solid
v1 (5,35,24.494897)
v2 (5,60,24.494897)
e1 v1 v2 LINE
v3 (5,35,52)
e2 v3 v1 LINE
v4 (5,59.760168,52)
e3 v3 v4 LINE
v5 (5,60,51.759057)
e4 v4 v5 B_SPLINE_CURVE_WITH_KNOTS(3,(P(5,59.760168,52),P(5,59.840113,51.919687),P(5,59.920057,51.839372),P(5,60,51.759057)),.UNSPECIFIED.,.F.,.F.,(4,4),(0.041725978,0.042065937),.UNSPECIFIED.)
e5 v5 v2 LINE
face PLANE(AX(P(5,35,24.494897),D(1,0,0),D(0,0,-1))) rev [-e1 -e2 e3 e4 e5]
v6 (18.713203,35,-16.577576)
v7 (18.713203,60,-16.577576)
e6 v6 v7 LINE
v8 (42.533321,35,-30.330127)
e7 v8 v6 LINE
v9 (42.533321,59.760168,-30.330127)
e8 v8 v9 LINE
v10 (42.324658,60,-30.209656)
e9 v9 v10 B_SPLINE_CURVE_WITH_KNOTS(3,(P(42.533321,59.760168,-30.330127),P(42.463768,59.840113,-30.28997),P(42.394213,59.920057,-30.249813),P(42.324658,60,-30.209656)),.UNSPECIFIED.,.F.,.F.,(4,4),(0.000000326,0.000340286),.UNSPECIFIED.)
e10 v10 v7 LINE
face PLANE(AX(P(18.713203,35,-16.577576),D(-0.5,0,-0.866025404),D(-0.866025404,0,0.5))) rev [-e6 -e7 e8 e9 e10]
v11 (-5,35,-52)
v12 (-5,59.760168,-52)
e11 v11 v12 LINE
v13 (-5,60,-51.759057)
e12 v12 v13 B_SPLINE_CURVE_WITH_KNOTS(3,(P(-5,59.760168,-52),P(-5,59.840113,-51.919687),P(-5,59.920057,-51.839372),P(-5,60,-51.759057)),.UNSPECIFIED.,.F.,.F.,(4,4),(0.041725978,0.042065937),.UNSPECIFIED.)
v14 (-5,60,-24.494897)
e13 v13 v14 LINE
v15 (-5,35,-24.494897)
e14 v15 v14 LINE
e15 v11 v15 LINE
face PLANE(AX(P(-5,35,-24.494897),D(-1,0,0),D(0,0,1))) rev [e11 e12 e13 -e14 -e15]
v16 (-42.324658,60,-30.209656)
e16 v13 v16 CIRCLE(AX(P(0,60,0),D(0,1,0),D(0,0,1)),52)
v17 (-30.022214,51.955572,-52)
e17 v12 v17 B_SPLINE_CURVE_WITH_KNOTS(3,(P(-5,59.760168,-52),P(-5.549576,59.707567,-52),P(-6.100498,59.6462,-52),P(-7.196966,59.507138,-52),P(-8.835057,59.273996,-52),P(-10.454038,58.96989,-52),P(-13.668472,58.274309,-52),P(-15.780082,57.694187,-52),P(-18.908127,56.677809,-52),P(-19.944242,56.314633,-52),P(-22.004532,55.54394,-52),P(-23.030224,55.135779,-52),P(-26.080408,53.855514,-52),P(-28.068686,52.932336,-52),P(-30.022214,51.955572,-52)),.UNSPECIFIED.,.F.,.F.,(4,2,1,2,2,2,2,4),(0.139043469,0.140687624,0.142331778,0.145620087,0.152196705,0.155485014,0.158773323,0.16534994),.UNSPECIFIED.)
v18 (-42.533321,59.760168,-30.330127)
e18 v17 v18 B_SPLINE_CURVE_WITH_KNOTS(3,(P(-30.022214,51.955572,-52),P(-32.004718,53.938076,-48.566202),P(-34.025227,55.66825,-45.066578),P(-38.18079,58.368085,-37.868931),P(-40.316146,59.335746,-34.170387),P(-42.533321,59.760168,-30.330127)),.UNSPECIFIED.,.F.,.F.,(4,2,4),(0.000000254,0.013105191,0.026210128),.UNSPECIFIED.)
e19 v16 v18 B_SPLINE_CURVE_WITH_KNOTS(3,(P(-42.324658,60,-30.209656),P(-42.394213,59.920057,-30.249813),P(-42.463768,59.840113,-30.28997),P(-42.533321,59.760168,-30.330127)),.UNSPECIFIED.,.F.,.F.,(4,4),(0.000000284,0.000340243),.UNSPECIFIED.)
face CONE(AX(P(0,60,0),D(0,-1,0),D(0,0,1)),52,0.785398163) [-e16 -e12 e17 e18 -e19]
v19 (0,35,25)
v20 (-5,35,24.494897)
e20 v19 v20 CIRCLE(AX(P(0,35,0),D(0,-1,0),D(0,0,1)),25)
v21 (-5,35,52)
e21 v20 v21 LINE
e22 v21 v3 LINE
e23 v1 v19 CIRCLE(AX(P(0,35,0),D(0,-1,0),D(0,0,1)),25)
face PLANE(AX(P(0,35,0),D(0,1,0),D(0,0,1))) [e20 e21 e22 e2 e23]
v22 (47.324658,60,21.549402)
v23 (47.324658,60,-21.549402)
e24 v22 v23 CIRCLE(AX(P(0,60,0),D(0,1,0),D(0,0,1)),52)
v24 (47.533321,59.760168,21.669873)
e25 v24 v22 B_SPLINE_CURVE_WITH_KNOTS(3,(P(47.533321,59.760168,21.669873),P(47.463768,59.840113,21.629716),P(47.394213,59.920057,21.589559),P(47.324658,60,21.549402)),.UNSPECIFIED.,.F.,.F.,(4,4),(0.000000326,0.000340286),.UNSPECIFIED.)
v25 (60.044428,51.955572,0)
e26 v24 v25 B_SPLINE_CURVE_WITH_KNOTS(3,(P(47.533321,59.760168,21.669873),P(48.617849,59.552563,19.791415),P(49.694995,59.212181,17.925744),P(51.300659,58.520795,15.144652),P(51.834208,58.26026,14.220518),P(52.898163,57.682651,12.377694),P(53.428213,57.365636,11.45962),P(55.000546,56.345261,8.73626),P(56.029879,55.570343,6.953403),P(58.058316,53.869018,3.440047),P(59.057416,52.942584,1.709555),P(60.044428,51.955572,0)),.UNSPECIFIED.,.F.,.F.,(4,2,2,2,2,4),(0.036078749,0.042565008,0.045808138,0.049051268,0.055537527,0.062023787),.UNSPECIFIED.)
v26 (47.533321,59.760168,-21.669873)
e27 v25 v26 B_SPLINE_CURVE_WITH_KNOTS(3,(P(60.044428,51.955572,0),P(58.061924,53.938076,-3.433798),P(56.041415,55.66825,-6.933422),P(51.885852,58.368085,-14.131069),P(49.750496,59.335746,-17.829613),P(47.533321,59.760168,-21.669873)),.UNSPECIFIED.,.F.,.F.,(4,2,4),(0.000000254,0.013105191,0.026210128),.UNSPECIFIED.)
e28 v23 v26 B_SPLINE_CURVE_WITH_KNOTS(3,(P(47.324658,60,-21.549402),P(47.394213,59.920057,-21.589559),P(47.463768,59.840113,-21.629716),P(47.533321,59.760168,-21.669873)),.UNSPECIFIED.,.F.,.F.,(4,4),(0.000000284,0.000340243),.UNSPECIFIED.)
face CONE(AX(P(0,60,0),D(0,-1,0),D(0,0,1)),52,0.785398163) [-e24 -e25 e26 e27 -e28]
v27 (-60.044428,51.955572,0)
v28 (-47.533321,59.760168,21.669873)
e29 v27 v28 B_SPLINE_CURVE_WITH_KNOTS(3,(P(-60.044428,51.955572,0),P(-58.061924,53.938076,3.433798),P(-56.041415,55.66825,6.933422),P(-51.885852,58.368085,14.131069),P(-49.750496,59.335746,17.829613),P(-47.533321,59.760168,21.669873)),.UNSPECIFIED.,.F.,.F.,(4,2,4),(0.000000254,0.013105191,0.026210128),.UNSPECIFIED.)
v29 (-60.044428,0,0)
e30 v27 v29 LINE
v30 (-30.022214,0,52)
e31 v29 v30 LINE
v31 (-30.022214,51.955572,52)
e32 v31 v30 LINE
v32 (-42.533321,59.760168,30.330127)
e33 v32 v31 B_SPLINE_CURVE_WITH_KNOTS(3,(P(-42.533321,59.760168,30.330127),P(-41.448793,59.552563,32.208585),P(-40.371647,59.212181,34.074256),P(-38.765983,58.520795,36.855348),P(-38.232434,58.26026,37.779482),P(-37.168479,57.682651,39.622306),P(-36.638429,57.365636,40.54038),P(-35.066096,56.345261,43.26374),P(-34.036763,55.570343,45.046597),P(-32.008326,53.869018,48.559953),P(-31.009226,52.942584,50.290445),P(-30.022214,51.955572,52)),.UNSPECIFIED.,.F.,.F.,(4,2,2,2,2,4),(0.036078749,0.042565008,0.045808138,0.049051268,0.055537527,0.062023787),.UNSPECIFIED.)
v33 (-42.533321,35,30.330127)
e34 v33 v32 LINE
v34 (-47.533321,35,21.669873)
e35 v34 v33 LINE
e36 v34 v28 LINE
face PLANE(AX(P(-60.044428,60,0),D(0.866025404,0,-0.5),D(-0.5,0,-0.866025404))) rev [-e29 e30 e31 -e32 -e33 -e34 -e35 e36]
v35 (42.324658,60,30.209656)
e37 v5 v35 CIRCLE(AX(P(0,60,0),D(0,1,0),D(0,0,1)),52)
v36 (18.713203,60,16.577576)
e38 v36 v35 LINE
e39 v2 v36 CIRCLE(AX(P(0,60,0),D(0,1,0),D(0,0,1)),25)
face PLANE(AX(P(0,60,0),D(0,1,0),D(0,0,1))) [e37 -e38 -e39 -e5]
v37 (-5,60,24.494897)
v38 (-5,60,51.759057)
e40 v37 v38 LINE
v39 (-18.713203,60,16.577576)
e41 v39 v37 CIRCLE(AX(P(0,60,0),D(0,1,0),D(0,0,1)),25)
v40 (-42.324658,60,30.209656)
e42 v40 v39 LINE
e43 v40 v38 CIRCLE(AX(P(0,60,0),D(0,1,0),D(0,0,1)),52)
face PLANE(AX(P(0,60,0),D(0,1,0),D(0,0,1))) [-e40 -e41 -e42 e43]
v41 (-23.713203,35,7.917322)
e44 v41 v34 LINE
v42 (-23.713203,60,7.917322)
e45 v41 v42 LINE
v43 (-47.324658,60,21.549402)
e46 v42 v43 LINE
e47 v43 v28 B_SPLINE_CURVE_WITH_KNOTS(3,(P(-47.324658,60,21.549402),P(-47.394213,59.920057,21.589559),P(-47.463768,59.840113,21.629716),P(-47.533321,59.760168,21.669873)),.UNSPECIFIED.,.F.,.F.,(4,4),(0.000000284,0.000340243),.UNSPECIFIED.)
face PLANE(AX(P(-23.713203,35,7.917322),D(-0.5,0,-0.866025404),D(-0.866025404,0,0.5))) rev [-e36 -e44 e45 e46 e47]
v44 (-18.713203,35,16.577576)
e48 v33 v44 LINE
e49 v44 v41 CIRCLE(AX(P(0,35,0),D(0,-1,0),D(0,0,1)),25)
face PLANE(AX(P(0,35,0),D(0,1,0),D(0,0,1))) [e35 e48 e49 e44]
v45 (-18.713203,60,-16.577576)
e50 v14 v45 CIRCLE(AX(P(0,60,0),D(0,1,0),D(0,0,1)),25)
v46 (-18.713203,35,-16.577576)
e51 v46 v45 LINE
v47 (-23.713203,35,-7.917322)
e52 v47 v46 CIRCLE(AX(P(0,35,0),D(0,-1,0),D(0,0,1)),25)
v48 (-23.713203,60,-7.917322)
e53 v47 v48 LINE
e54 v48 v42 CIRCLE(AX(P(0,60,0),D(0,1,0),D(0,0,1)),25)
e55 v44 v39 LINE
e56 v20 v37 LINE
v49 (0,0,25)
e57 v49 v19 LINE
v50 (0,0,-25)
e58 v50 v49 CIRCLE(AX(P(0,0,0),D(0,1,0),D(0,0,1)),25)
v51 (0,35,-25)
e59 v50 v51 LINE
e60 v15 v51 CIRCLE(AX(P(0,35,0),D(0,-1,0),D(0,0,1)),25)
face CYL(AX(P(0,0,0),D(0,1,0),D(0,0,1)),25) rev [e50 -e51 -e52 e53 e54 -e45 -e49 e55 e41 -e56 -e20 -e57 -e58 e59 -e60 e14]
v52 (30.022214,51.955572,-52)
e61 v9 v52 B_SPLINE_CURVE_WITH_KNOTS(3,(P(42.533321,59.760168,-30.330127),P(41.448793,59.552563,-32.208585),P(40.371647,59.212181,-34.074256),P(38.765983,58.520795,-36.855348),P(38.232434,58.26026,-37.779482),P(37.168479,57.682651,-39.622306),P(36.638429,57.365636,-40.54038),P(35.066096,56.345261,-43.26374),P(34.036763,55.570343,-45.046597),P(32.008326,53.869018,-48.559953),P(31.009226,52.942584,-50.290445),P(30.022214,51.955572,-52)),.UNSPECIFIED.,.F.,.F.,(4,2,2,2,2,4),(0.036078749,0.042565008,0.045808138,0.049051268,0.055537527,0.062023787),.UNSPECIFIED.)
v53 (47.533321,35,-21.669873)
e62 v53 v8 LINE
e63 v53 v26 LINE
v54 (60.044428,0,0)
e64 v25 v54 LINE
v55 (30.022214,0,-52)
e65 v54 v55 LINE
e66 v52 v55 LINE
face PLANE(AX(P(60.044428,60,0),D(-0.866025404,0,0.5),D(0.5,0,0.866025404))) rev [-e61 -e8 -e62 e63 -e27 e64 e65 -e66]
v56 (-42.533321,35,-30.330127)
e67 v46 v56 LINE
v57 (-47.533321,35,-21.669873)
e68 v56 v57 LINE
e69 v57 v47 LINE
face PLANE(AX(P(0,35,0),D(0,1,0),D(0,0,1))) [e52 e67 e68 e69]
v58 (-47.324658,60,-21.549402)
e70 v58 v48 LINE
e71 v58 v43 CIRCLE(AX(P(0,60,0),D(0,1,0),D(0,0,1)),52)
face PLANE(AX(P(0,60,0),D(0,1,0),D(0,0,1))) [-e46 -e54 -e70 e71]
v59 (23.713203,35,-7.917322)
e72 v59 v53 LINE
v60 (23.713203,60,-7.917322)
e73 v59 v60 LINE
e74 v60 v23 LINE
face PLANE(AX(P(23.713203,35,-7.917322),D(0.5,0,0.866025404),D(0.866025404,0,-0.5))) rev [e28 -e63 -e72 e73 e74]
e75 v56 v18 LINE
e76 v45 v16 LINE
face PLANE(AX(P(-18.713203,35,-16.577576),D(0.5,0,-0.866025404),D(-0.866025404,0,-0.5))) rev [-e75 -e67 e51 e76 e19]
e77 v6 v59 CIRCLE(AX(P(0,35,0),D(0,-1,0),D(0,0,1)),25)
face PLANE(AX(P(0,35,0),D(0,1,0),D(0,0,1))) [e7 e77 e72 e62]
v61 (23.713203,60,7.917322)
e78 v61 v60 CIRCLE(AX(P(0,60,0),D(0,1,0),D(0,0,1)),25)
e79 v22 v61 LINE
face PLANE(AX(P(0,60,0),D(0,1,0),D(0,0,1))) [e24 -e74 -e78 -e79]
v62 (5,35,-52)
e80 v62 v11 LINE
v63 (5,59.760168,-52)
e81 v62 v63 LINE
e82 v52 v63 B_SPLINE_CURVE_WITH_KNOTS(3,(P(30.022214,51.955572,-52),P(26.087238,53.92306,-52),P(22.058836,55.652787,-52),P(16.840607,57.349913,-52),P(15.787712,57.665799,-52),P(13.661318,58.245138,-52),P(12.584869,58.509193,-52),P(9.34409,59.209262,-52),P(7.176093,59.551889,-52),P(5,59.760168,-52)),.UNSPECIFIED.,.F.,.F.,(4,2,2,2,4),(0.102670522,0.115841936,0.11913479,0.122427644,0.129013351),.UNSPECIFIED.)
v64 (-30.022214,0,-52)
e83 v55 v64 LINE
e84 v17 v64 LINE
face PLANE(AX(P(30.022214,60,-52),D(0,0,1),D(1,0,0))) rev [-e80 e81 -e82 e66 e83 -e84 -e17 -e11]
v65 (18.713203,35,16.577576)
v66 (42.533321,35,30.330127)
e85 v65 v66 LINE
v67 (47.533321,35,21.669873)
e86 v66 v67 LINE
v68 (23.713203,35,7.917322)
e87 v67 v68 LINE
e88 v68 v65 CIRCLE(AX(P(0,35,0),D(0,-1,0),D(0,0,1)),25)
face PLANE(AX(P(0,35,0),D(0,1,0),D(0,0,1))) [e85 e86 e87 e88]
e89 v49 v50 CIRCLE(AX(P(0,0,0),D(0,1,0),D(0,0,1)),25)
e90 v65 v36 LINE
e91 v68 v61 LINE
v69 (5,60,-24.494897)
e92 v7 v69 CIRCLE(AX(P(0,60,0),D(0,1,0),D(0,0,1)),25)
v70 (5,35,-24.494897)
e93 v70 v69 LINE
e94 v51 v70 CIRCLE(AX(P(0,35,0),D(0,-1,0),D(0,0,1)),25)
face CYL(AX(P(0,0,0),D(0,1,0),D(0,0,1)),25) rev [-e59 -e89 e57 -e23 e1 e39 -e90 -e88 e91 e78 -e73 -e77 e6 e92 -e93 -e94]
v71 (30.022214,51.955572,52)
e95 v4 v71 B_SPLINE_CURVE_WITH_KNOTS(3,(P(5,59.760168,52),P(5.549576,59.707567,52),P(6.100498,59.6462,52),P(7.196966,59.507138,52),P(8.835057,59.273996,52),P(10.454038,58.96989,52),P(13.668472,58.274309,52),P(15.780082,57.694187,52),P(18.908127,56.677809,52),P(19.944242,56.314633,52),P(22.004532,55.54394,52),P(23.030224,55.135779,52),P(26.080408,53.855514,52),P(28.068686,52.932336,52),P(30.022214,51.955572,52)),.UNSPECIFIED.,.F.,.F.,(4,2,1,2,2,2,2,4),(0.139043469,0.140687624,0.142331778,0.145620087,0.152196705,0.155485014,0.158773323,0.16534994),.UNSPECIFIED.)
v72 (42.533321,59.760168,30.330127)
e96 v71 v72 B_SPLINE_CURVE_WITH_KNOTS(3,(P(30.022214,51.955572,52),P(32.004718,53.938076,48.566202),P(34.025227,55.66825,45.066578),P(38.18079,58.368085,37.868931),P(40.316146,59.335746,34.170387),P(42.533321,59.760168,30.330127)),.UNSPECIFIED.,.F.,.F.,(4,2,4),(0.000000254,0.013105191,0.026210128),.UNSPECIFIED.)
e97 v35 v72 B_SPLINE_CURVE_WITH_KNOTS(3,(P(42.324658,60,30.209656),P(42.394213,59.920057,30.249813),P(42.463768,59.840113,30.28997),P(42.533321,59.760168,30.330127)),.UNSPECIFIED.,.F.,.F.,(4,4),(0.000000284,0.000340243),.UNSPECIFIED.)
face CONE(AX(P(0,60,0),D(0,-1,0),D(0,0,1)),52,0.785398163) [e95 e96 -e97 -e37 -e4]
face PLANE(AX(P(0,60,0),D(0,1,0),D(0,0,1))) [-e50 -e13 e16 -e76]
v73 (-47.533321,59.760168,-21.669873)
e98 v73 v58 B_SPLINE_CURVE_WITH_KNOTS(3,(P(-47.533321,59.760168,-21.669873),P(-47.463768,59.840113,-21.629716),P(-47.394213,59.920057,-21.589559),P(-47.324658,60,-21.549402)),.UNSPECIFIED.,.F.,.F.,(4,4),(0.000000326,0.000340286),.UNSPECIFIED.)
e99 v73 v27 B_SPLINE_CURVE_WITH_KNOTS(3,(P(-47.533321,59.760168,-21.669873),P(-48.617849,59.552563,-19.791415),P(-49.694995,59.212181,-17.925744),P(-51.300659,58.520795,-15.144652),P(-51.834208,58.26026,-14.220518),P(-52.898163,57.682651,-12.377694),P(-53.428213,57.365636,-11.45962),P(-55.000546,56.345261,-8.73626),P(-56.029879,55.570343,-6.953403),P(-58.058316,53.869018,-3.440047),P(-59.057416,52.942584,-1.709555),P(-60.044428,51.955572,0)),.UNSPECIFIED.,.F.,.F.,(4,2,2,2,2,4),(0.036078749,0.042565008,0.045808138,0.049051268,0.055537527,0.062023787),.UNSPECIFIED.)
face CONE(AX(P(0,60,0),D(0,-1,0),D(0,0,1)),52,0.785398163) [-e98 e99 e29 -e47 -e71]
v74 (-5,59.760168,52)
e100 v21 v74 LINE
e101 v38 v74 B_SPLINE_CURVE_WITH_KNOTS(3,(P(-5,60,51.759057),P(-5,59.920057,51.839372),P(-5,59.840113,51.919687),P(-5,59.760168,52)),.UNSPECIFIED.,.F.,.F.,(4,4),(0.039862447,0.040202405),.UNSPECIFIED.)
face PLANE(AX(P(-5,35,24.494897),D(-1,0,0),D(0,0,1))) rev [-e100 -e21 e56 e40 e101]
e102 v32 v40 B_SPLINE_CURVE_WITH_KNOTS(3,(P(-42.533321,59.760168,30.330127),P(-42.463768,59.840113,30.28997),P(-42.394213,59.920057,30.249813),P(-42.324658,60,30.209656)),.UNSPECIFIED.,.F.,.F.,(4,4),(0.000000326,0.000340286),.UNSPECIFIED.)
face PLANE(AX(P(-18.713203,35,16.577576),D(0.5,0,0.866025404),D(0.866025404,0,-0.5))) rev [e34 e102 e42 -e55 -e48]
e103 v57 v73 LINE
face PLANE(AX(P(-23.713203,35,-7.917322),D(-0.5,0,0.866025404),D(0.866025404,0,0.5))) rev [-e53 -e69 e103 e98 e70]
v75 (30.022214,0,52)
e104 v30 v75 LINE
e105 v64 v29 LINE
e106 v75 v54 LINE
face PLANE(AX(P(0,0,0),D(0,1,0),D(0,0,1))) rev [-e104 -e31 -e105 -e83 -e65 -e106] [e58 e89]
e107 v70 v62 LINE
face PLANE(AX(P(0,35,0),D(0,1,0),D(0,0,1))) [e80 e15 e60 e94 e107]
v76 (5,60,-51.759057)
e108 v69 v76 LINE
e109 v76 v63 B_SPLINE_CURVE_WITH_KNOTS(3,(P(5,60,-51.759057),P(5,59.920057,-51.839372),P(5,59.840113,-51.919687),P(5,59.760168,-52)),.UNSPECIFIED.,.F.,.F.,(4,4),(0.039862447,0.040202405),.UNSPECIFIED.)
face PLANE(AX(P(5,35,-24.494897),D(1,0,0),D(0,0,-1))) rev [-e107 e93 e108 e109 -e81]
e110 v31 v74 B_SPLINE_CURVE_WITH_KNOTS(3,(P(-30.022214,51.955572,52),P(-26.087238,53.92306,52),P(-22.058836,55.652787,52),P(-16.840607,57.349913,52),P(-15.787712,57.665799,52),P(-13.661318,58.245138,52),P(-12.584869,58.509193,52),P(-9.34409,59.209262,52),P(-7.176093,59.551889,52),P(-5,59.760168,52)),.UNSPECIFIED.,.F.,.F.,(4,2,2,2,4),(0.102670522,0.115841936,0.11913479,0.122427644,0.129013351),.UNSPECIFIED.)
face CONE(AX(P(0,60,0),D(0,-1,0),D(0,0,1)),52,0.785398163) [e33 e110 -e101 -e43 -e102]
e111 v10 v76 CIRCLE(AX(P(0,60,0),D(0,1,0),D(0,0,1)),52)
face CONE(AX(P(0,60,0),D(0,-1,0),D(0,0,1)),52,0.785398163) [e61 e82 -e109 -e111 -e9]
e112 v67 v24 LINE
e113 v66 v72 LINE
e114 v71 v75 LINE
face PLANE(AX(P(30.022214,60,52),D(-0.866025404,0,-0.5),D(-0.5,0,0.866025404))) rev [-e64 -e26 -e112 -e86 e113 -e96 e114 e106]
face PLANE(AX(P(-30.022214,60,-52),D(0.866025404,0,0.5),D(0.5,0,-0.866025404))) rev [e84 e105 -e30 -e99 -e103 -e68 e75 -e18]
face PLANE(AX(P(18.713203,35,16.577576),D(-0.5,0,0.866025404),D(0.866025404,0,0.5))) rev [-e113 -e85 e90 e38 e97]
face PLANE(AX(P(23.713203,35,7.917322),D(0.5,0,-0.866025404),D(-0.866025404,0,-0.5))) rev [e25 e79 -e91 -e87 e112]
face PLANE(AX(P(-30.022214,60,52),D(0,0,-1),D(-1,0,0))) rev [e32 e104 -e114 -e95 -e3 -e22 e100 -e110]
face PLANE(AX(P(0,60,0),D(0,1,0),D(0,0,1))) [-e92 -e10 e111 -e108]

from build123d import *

# Parameters (mm, degrees)
HEX_BODY_104AF_X_60_DEPTH      = 60
CROWN_CHAMFER_SKETCH_OUTSIDE_W = 276.052
CROWN_CHAMFER_SKETCH_OUTSIDE_H = 259.964
CROWN_CHAMFER_SKETCH_OUTSIDE_R = 52
CROWN_CHAMFER_45DEG_DEPTH      = 60
CROWN_CHAMFER_45DEG_DRAFT      = -45
BORE_SKETCH_50_R               = 25
BORE_50_DEPTH                  = 60
CASTLE_SLOTS_6X10_DEPTH        = 25


with BuildPart() as part:
    # Hex Profile Sketch → Hex Body 104AF x 60 (new body)
    with BuildSketch(Plane(origin=(0, 0, 0), x_dir=(1, 0, 0), z_dir=(0, 1, 0))):
        Polygon((30.022213998, -52), (60.044427996, 0), (30.022213998, 52), (-30.022213998, 52), (-60.044427996, 0), (-30.022213998, -52), align=None)
    extrude(amount=HEX_BODY_104AF_X_60_DEPTH)


with BuildPart() as crown_chamfer_45deg_tool:
    # Crown Chamfer Sketch outside → Crown Chamfer 45deg (with draft: the straight prism first)
    with BuildSketch(Plane(origin=(0, 60, 0), x_dir=(1, 0, 0), z_dir=(0, 1, 0))):
        Rectangle(CROWN_CHAMFER_SKETCH_OUTSIDE_W, CROWN_CHAMFER_SKETCH_OUTSIDE_H)
        Circle(CROWN_CHAMFER_SKETCH_OUTSIDE_R, mode=Mode.SUBTRACT)
    extrude(amount=-CROWN_CHAMFER_45DEG_DEPTH)
    # Crown Chamfer 45deg: the draft: its side faces are tilted about the plane it starts from
    crown_chamfer_45deg_sides = [crown_chamfer_45deg_tool.faces().sort_by_distance(p)[0] for p in [
        (0, 30, 129.982),
        (138.026, 30, 0),
        (0, 30, -129.982),
        (-138.026, 30, 0),
        (-52, 30, 0),
    ]]
    draft(crown_chamfer_45deg_sides, Plane(origin=(0, 60, 0), x_dir=(1, 0, 0), z_dir=(0, 1, 0)), CROWN_CHAMFER_45DEG_DRAFT)


with BuildPart() as part_1:
    add(part.part)

    # Crown Chamfer 45deg: cut by crown_chamfer_45deg_tool
    add(crown_chamfer_45deg_tool.part, mode=Mode.SUBTRACT)

    # Bore Sketch Ø50 → Bore Ø50 (cut)
    with BuildSketch(Plane(origin=(0, 60, 0), x_dir=(1, 0, 0), z_dir=(0, 1, 0))):
        with Locations(Location((0, 0, 0), (0, 0, 270))):
            Circle(BORE_SKETCH_50_R)
    extrude(amount=-BORE_50_DEPTH, mode=Mode.SUBTRACT)

    # Castle Slots Sketch → Castle Slots 6x10 (cut)
    with BuildSketch(Plane(origin=(0, 60, 0), x_dir=(1, 0, 0), z_dir=(0, 1, 0))):
        with BuildLine():
            Line((-5, -24.494897428), (-5, -52))
            Line((-5, -52), (0, -52))
            Line((0, -52), (5, -52))
            Line((5, -52), (5, -24.494897428))
            ThreePointArc((5, -24.494897428), (0, -25), (-5, -24.494897428))
        make_face()
        with BuildLine():
            Line((-23.713203436, -7.917321695), (-47.533320997, -21.669872981))
            Line((-47.533320997, -21.669872981), (-45.033320997, -26))
            Line((-45.033320997, -26), (-42.533320997, -30.330127019))
            Line((-42.533320997, -30.330127019), (-18.713203436, -16.577575733))
            ThreePointArc((-18.713203436, -16.577575733), (-21.650635095, -12.5), (-23.713203436, -7.917321695))
        make_face()
        with BuildLine():
            Line((-18.713203436, 16.577575733), (-42.533320997, 30.330127019))
            Line((-42.533320997, 30.330127019), (-45.033320997, 26))
            Line((-45.033320997, 26), (-47.533320997, 21.669872981))
            Line((-47.533320997, 21.669872981), (-23.713203436, 7.917321695))
            ThreePointArc((-23.713203436, 7.917321695), (-21.650635095, 12.5), (-18.713203436, 16.577575733))
        make_face()
        with BuildLine():
            Line((5, 24.494897428), (5, 52))
            Line((5, 52), (0, 52))
            Line((0, 52), (-5, 52))
            Line((-5, 52), (-5, 24.494897428))
            ThreePointArc((-5, 24.494897428), (0, 25), (5, 24.494897428))
        make_face()
        with BuildLine():
            Line((23.713203436, 7.917321695), (47.533320997, 21.669872981))
            Line((47.533320997, 21.669872981), (45.033320997, 26))
            Line((45.033320997, 26), (42.533320997, 30.330127019))
            Line((42.533320997, 30.330127019), (18.713203436, 16.577575733))
            ThreePointArc((18.713203436, 16.577575733), (21.650635095, 12.5), (23.713203436, 7.917321695))
        make_face()
        with BuildLine():
            Line((18.713203436, -16.577575733), (42.533320997, -30.330127019))
            Line((42.533320997, -30.330127019), (45.033320997, -26))
            Line((45.033320997, -26), (47.533320997, -21.669872981))
            Line((47.533320997, -21.669872981), (23.713203436, -7.917321695))
            ThreePointArc((23.713203436, -7.917321695), (21.650635095, -12.5), (18.713203436, -16.577575733))
        make_face()
    extrude(amount=-CASTLE_SLOTS_6X10_DEPTH, mode=Mode.SUBTRACT)


solid = part_1.part
